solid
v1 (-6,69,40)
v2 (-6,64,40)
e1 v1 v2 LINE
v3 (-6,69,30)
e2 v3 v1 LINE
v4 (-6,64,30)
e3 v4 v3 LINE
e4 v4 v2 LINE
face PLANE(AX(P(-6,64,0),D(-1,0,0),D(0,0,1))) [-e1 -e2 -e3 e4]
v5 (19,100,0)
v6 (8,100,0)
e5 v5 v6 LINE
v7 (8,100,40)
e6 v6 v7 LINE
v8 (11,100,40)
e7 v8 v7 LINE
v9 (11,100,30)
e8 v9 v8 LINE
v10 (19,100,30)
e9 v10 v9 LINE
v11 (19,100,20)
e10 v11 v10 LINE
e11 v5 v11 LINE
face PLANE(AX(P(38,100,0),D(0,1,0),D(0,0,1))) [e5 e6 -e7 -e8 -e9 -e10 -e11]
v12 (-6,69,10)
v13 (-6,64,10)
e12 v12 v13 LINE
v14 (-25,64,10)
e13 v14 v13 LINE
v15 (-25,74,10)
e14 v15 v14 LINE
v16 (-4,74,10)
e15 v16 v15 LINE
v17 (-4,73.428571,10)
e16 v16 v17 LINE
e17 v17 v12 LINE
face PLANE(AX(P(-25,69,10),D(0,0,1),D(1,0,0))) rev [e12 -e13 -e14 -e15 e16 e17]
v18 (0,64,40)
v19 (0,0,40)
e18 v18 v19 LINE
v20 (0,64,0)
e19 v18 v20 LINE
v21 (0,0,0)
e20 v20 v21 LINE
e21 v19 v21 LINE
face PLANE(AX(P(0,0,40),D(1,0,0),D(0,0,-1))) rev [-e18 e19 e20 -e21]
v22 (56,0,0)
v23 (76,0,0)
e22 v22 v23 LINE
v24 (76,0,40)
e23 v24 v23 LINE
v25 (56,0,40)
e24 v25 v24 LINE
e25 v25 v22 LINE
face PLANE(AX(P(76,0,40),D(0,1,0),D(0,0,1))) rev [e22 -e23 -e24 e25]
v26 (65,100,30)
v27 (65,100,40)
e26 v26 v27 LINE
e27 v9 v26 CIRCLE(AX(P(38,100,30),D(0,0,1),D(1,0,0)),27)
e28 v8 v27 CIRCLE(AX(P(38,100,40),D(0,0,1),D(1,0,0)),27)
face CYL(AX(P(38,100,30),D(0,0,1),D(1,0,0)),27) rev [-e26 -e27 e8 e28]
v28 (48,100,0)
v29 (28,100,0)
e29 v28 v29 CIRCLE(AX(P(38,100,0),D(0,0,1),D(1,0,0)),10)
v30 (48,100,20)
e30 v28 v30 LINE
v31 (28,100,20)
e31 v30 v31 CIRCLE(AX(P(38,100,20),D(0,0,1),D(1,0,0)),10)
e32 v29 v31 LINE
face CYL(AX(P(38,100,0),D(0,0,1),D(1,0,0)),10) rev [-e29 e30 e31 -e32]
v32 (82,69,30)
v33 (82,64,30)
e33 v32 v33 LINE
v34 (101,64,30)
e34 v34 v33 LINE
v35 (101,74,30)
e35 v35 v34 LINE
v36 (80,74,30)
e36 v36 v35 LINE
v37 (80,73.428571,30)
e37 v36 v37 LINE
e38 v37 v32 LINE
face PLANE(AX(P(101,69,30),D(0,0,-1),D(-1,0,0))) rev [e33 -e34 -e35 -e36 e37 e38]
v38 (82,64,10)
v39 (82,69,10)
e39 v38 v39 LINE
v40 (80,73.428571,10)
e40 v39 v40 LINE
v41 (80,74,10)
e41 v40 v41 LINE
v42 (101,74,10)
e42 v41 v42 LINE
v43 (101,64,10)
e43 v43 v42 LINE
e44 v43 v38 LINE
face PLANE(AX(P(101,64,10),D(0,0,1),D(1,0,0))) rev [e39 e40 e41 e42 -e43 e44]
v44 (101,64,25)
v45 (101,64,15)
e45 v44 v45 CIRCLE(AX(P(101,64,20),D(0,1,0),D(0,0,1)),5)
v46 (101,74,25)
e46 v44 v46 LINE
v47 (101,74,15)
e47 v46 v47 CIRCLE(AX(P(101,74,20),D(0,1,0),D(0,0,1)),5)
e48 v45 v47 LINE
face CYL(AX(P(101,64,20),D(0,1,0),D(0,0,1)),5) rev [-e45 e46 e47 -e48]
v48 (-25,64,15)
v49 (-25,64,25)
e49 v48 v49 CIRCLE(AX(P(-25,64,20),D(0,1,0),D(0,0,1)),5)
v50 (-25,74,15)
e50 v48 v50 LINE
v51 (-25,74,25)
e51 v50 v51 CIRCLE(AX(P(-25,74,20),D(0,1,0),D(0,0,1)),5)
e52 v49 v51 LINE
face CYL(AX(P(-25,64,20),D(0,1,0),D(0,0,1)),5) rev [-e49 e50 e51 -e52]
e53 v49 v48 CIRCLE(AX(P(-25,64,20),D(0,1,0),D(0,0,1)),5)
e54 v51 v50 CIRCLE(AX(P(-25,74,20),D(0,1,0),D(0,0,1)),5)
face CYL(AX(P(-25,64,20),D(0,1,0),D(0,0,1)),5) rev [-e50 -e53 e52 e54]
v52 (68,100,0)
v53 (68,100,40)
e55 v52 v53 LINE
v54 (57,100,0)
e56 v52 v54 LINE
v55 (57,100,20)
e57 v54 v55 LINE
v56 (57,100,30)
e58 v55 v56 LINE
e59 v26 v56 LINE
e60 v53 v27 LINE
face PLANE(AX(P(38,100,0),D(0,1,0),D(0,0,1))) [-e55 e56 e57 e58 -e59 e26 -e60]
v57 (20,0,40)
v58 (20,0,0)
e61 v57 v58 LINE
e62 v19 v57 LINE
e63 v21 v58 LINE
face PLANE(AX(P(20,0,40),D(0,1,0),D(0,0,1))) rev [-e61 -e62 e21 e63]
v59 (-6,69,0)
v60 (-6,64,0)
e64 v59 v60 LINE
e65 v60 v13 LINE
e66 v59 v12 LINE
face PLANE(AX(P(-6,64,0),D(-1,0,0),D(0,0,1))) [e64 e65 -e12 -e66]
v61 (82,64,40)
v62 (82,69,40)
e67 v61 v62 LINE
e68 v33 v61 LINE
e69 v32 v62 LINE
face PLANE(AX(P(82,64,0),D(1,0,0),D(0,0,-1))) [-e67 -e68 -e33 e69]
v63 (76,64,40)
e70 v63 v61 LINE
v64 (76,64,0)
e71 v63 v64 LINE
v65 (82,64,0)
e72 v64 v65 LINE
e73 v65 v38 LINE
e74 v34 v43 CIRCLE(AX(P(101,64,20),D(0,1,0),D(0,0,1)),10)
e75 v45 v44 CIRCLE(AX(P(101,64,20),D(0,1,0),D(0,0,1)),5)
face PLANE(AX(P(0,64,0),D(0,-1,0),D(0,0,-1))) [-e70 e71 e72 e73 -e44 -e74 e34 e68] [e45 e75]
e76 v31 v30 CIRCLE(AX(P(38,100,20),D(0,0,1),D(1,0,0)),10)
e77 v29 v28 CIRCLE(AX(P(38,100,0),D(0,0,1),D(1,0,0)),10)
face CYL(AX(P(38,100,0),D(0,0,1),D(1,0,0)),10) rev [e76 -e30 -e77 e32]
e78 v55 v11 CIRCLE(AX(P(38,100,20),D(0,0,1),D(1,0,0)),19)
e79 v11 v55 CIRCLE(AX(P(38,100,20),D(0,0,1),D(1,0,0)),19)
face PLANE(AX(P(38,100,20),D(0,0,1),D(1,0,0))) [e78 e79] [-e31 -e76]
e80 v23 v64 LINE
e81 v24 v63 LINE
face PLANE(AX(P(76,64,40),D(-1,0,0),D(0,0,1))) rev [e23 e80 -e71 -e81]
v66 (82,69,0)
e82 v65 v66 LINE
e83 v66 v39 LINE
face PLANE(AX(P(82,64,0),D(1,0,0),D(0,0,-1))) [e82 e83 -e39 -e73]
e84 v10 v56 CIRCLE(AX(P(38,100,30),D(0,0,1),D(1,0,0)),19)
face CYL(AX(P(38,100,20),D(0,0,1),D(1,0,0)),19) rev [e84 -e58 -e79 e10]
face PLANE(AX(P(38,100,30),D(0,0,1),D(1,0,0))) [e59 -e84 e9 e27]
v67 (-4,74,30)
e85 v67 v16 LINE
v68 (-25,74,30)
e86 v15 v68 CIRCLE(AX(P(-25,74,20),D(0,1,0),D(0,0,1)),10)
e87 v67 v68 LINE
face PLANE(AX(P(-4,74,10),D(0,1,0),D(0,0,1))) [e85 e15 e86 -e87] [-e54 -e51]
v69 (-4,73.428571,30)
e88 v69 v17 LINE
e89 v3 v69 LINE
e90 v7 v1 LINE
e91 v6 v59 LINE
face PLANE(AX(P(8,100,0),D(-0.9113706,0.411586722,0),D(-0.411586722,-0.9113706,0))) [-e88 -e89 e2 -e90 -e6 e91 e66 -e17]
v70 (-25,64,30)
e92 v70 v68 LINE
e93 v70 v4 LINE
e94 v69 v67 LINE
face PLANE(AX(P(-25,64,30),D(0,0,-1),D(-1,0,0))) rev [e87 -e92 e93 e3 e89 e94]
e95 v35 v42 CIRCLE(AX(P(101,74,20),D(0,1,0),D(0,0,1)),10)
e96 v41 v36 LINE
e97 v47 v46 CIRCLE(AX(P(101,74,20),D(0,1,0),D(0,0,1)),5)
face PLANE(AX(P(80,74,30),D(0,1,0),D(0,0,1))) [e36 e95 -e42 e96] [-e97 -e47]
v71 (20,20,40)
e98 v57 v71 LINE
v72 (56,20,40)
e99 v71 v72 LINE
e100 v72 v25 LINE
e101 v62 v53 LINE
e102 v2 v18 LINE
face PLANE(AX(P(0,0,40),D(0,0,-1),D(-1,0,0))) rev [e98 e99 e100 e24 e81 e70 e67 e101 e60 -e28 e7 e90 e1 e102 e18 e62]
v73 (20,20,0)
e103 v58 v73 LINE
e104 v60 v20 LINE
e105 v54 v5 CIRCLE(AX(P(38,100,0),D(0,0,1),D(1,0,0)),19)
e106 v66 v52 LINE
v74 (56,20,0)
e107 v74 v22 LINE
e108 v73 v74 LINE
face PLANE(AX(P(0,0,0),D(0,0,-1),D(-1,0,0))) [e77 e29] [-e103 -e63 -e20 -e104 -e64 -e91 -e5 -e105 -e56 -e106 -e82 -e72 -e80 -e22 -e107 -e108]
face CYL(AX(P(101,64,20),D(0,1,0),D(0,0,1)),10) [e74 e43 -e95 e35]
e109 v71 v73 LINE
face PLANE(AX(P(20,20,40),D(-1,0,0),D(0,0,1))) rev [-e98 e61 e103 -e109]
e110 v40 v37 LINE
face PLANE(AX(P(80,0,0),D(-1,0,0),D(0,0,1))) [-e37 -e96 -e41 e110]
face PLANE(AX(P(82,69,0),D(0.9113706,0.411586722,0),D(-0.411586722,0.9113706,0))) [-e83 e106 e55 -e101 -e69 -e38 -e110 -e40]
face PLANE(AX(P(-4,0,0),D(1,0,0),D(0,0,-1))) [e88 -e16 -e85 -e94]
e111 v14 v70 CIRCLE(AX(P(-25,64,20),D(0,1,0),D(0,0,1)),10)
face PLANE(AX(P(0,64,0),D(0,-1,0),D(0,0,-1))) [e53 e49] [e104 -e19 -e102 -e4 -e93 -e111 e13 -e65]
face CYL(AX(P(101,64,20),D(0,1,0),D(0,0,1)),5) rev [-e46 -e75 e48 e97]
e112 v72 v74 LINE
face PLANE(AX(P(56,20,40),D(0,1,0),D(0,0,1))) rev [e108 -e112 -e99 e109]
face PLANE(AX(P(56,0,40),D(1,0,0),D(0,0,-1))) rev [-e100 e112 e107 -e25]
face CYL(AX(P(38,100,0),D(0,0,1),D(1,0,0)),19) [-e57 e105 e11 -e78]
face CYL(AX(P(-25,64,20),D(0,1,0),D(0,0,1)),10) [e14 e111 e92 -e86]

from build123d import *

# Parameters (mm, degrees)
BASE_BODY_DEPTH             = 40
UPPER_BODY_DEPTH            = 40
LEFT_LUG_BLOCK_SKETCH_W     = 20
LEFT_LUG_BLOCK_SKETCH_H     = 5
LEFT_LUG_BLOCK_DEPTH        = 19
LEFT_LUG_ARM_SKETCH_W       = 20
LEFT_LUG_ARM_SKETCH_H       = 5
LEFT_LUG_ARM_DEPTH          = 21
LEFT_LUG_ROUNDED_END_DEPTH  = 10
LEFT_LUG_HOLE_SKETCH_R      = 5
LEFT_LUG_HOLE_10_DEPTH      = 10
RIGHT_LUG_BLOCK_SKETCH_W    = 20
RIGHT_LUG_BLOCK_SKETCH_H    = 5
RIGHT_LUG_BLOCK_DEPTH       = 19
RIGHT_LUG_ARM_SKETCH_W      = 20
RIGHT_LUG_ARM_SKETCH_H      = 5
RIGHT_LUG_ARM_DEPTH         = 21
RIGHT_LUG_ROUNDED_END_DEPTH = 10
RIGHT_LUG_HOLE_SKETCH_R     = 5
RIGHT_LUG_HOLE_10_DEPTH     = 10
BEARING_SEAT_CUT_54_DEPTH   = 10
SEAT_GROOVE_38_DEPTH        = 30
HUB_SKETCH_R                = 19
HUB_38_DEPTH                = 30
HUB_RECESS_SKETCH_R         = 19
HUB_RECESS_38_DEPTH         = 10
BORE_SKETCH_R               = 10
BORE_20_DEPTH               = 20


with BuildPart() as part:
    # Base Body Sketch → Base Body (new body)
    with BuildSketch(Plane.XY):
        Polygon((0, 0), (0, 64), (76, 64), (76, 0), (56, 0), (56, 20), (20, 20), (20, 0), align=None)
    extrude(amount=BASE_BODY_DEPTH)

    # Upper Body Sketch → Upper Body (add)
    with BuildSketch(Plane.XY.offset(40)):
        Polygon((0, 64), (-6, 64), (-6, 69), (8, 100), (38, 100), (68, 100), (82, 69), (82, 64), (76, 64), align=None)
    extrude(amount=-UPPER_BODY_DEPTH)

    # Left Lug Block Sketch → Left Lug Block (add)
    with BuildSketch(Plane.ZY.offset(6)):
        with Locations((20, 66.5)):
            Rectangle(LEFT_LUG_BLOCK_SKETCH_W, LEFT_LUG_BLOCK_SKETCH_H)
    extrude(amount=LEFT_LUG_BLOCK_DEPTH)

    # Left Lug Arm Sketch → Left Lug Arm (add)
    with BuildSketch(Plane.ZY.offset(25)):
        with Locations((20, 71.5)):
            Rectangle(LEFT_LUG_ARM_SKETCH_W, LEFT_LUG_ARM_SKETCH_H)
    extrude(amount=-LEFT_LUG_ARM_DEPTH)

    # Left Lug End Sketch → Left Lug Rounded End (add)
    with BuildSketch(Plane(origin=(0, 74, 0), x_dir=(1, 0, 0), z_dir=(0, 1, 0))):
        with BuildLine():
            Line((-25, -10), (-25, -30))
            ThreePointArc((-25, -30), (-35, -20), (-25, -10))
        make_face()
    extrude(amount=-LEFT_LUG_ROUNDED_END_DEPTH)

    # Left Lug Hole Sketch → Left Lug Hole Ø10 (cut)
    with BuildSketch(Plane(origin=(0, 74, 0), x_dir=(1, 0, 0), z_dir=(0, 1, 0))):
        with Locations(Location((-25, -20, 0), (0, 0, 270))):
            Circle(LEFT_LUG_HOLE_SKETCH_R)
    extrude(amount=-LEFT_LUG_HOLE_10_DEPTH, mode=Mode.SUBTRACT)

    # Right Lug Block Sketch → Right Lug Block (add)
    with BuildSketch(Plane(origin=(82, 0, 0), x_dir=(0, 0, -1), z_dir=(1, 0, 0))):
        with Locations((-20, 66.5)):
            Rectangle(RIGHT_LUG_BLOCK_SKETCH_W, RIGHT_LUG_BLOCK_SKETCH_H)
    extrude(amount=RIGHT_LUG_BLOCK_DEPTH)

    # Right Lug Arm Sketch → Right Lug Arm (add)
    with BuildSketch(Plane(origin=(101, 0, 0), x_dir=(0, 0, -1), z_dir=(1, 0, 0))):
        with Locations((-20, 71.5)):
            Rectangle(RIGHT_LUG_ARM_SKETCH_W, RIGHT_LUG_ARM_SKETCH_H)
    extrude(amount=-RIGHT_LUG_ARM_DEPTH)

    # Right Lug End Sketch → Right Lug Rounded End (add)
    with BuildSketch(Plane(origin=(0, 74, 0), x_dir=(1, 0, 0), z_dir=(0, 1, 0))):
        with BuildLine():
            Line((101, -10), (101, -30))
            ThreePointArc((101, -30), (111, -20), (101, -10))
        make_face()
    extrude(amount=-RIGHT_LUG_ROUNDED_END_DEPTH)

    # Right Lug Hole Sketch → Right Lug Hole Ø10 (cut)
    with BuildSketch(Plane(origin=(0, 74, 0), x_dir=(1, 0, 0), z_dir=(0, 1, 0))):
        with Locations(Location((101, -20, 0), (0, 0, 270))):
            Circle(RIGHT_LUG_HOLE_SKETCH_R)
    extrude(amount=-RIGHT_LUG_HOLE_10_DEPTH, mode=Mode.SUBTRACT)

    # Bearing Seat Sketch → Bearing Seat Cut Ø54 (cut)
    with BuildSketch(Plane.XY.offset(40)):
        with BuildLine():
            Line((11, 100), (65, 100))
            ThreePointArc((65, 100), (38, 73), (11, 100))
        make_face()
    extrude(amount=-BEARING_SEAT_CUT_54_DEPTH, mode=Mode.SUBTRACT)

    # Seat Groove Sketch → Seat Groove Ø38 (cut)
    with BuildSketch(Plane.XY.offset(30)):
        with BuildLine():
            Line((19, 100), (57, 100))
            ThreePointArc((57, 100), (38, 81), (19, 100))
        make_face()
    extrude(amount=-SEAT_GROOVE_38_DEPTH, mode=Mode.SUBTRACT)

    # Hub Sketch → Hub Ø38 (add)
    with BuildSketch(Plane.XY.offset(30)):
        with Locations((38, 100)):
            Circle(HUB_SKETCH_R)
    extrude(amount=-HUB_38_DEPTH)

    # Hub Recess Sketch → Hub Recess Ø38 (cut)
    with BuildSketch(Plane.XY.offset(30)):
        with Locations((38, 100)):
            Circle(HUB_RECESS_SKETCH_R)
    extrude(amount=-HUB_RECESS_38_DEPTH, mode=Mode.SUBTRACT)

    # Bore Sketch → Bore Ø20 (cut)
    with BuildSketch(Plane.XY.offset(20)):
        with Locations((38, 100)):
            Circle(BORE_SKETCH_R)
    extrude(amount=-BORE_20_DEPTH, mode=Mode.SUBTRACT)


solid = part.part
